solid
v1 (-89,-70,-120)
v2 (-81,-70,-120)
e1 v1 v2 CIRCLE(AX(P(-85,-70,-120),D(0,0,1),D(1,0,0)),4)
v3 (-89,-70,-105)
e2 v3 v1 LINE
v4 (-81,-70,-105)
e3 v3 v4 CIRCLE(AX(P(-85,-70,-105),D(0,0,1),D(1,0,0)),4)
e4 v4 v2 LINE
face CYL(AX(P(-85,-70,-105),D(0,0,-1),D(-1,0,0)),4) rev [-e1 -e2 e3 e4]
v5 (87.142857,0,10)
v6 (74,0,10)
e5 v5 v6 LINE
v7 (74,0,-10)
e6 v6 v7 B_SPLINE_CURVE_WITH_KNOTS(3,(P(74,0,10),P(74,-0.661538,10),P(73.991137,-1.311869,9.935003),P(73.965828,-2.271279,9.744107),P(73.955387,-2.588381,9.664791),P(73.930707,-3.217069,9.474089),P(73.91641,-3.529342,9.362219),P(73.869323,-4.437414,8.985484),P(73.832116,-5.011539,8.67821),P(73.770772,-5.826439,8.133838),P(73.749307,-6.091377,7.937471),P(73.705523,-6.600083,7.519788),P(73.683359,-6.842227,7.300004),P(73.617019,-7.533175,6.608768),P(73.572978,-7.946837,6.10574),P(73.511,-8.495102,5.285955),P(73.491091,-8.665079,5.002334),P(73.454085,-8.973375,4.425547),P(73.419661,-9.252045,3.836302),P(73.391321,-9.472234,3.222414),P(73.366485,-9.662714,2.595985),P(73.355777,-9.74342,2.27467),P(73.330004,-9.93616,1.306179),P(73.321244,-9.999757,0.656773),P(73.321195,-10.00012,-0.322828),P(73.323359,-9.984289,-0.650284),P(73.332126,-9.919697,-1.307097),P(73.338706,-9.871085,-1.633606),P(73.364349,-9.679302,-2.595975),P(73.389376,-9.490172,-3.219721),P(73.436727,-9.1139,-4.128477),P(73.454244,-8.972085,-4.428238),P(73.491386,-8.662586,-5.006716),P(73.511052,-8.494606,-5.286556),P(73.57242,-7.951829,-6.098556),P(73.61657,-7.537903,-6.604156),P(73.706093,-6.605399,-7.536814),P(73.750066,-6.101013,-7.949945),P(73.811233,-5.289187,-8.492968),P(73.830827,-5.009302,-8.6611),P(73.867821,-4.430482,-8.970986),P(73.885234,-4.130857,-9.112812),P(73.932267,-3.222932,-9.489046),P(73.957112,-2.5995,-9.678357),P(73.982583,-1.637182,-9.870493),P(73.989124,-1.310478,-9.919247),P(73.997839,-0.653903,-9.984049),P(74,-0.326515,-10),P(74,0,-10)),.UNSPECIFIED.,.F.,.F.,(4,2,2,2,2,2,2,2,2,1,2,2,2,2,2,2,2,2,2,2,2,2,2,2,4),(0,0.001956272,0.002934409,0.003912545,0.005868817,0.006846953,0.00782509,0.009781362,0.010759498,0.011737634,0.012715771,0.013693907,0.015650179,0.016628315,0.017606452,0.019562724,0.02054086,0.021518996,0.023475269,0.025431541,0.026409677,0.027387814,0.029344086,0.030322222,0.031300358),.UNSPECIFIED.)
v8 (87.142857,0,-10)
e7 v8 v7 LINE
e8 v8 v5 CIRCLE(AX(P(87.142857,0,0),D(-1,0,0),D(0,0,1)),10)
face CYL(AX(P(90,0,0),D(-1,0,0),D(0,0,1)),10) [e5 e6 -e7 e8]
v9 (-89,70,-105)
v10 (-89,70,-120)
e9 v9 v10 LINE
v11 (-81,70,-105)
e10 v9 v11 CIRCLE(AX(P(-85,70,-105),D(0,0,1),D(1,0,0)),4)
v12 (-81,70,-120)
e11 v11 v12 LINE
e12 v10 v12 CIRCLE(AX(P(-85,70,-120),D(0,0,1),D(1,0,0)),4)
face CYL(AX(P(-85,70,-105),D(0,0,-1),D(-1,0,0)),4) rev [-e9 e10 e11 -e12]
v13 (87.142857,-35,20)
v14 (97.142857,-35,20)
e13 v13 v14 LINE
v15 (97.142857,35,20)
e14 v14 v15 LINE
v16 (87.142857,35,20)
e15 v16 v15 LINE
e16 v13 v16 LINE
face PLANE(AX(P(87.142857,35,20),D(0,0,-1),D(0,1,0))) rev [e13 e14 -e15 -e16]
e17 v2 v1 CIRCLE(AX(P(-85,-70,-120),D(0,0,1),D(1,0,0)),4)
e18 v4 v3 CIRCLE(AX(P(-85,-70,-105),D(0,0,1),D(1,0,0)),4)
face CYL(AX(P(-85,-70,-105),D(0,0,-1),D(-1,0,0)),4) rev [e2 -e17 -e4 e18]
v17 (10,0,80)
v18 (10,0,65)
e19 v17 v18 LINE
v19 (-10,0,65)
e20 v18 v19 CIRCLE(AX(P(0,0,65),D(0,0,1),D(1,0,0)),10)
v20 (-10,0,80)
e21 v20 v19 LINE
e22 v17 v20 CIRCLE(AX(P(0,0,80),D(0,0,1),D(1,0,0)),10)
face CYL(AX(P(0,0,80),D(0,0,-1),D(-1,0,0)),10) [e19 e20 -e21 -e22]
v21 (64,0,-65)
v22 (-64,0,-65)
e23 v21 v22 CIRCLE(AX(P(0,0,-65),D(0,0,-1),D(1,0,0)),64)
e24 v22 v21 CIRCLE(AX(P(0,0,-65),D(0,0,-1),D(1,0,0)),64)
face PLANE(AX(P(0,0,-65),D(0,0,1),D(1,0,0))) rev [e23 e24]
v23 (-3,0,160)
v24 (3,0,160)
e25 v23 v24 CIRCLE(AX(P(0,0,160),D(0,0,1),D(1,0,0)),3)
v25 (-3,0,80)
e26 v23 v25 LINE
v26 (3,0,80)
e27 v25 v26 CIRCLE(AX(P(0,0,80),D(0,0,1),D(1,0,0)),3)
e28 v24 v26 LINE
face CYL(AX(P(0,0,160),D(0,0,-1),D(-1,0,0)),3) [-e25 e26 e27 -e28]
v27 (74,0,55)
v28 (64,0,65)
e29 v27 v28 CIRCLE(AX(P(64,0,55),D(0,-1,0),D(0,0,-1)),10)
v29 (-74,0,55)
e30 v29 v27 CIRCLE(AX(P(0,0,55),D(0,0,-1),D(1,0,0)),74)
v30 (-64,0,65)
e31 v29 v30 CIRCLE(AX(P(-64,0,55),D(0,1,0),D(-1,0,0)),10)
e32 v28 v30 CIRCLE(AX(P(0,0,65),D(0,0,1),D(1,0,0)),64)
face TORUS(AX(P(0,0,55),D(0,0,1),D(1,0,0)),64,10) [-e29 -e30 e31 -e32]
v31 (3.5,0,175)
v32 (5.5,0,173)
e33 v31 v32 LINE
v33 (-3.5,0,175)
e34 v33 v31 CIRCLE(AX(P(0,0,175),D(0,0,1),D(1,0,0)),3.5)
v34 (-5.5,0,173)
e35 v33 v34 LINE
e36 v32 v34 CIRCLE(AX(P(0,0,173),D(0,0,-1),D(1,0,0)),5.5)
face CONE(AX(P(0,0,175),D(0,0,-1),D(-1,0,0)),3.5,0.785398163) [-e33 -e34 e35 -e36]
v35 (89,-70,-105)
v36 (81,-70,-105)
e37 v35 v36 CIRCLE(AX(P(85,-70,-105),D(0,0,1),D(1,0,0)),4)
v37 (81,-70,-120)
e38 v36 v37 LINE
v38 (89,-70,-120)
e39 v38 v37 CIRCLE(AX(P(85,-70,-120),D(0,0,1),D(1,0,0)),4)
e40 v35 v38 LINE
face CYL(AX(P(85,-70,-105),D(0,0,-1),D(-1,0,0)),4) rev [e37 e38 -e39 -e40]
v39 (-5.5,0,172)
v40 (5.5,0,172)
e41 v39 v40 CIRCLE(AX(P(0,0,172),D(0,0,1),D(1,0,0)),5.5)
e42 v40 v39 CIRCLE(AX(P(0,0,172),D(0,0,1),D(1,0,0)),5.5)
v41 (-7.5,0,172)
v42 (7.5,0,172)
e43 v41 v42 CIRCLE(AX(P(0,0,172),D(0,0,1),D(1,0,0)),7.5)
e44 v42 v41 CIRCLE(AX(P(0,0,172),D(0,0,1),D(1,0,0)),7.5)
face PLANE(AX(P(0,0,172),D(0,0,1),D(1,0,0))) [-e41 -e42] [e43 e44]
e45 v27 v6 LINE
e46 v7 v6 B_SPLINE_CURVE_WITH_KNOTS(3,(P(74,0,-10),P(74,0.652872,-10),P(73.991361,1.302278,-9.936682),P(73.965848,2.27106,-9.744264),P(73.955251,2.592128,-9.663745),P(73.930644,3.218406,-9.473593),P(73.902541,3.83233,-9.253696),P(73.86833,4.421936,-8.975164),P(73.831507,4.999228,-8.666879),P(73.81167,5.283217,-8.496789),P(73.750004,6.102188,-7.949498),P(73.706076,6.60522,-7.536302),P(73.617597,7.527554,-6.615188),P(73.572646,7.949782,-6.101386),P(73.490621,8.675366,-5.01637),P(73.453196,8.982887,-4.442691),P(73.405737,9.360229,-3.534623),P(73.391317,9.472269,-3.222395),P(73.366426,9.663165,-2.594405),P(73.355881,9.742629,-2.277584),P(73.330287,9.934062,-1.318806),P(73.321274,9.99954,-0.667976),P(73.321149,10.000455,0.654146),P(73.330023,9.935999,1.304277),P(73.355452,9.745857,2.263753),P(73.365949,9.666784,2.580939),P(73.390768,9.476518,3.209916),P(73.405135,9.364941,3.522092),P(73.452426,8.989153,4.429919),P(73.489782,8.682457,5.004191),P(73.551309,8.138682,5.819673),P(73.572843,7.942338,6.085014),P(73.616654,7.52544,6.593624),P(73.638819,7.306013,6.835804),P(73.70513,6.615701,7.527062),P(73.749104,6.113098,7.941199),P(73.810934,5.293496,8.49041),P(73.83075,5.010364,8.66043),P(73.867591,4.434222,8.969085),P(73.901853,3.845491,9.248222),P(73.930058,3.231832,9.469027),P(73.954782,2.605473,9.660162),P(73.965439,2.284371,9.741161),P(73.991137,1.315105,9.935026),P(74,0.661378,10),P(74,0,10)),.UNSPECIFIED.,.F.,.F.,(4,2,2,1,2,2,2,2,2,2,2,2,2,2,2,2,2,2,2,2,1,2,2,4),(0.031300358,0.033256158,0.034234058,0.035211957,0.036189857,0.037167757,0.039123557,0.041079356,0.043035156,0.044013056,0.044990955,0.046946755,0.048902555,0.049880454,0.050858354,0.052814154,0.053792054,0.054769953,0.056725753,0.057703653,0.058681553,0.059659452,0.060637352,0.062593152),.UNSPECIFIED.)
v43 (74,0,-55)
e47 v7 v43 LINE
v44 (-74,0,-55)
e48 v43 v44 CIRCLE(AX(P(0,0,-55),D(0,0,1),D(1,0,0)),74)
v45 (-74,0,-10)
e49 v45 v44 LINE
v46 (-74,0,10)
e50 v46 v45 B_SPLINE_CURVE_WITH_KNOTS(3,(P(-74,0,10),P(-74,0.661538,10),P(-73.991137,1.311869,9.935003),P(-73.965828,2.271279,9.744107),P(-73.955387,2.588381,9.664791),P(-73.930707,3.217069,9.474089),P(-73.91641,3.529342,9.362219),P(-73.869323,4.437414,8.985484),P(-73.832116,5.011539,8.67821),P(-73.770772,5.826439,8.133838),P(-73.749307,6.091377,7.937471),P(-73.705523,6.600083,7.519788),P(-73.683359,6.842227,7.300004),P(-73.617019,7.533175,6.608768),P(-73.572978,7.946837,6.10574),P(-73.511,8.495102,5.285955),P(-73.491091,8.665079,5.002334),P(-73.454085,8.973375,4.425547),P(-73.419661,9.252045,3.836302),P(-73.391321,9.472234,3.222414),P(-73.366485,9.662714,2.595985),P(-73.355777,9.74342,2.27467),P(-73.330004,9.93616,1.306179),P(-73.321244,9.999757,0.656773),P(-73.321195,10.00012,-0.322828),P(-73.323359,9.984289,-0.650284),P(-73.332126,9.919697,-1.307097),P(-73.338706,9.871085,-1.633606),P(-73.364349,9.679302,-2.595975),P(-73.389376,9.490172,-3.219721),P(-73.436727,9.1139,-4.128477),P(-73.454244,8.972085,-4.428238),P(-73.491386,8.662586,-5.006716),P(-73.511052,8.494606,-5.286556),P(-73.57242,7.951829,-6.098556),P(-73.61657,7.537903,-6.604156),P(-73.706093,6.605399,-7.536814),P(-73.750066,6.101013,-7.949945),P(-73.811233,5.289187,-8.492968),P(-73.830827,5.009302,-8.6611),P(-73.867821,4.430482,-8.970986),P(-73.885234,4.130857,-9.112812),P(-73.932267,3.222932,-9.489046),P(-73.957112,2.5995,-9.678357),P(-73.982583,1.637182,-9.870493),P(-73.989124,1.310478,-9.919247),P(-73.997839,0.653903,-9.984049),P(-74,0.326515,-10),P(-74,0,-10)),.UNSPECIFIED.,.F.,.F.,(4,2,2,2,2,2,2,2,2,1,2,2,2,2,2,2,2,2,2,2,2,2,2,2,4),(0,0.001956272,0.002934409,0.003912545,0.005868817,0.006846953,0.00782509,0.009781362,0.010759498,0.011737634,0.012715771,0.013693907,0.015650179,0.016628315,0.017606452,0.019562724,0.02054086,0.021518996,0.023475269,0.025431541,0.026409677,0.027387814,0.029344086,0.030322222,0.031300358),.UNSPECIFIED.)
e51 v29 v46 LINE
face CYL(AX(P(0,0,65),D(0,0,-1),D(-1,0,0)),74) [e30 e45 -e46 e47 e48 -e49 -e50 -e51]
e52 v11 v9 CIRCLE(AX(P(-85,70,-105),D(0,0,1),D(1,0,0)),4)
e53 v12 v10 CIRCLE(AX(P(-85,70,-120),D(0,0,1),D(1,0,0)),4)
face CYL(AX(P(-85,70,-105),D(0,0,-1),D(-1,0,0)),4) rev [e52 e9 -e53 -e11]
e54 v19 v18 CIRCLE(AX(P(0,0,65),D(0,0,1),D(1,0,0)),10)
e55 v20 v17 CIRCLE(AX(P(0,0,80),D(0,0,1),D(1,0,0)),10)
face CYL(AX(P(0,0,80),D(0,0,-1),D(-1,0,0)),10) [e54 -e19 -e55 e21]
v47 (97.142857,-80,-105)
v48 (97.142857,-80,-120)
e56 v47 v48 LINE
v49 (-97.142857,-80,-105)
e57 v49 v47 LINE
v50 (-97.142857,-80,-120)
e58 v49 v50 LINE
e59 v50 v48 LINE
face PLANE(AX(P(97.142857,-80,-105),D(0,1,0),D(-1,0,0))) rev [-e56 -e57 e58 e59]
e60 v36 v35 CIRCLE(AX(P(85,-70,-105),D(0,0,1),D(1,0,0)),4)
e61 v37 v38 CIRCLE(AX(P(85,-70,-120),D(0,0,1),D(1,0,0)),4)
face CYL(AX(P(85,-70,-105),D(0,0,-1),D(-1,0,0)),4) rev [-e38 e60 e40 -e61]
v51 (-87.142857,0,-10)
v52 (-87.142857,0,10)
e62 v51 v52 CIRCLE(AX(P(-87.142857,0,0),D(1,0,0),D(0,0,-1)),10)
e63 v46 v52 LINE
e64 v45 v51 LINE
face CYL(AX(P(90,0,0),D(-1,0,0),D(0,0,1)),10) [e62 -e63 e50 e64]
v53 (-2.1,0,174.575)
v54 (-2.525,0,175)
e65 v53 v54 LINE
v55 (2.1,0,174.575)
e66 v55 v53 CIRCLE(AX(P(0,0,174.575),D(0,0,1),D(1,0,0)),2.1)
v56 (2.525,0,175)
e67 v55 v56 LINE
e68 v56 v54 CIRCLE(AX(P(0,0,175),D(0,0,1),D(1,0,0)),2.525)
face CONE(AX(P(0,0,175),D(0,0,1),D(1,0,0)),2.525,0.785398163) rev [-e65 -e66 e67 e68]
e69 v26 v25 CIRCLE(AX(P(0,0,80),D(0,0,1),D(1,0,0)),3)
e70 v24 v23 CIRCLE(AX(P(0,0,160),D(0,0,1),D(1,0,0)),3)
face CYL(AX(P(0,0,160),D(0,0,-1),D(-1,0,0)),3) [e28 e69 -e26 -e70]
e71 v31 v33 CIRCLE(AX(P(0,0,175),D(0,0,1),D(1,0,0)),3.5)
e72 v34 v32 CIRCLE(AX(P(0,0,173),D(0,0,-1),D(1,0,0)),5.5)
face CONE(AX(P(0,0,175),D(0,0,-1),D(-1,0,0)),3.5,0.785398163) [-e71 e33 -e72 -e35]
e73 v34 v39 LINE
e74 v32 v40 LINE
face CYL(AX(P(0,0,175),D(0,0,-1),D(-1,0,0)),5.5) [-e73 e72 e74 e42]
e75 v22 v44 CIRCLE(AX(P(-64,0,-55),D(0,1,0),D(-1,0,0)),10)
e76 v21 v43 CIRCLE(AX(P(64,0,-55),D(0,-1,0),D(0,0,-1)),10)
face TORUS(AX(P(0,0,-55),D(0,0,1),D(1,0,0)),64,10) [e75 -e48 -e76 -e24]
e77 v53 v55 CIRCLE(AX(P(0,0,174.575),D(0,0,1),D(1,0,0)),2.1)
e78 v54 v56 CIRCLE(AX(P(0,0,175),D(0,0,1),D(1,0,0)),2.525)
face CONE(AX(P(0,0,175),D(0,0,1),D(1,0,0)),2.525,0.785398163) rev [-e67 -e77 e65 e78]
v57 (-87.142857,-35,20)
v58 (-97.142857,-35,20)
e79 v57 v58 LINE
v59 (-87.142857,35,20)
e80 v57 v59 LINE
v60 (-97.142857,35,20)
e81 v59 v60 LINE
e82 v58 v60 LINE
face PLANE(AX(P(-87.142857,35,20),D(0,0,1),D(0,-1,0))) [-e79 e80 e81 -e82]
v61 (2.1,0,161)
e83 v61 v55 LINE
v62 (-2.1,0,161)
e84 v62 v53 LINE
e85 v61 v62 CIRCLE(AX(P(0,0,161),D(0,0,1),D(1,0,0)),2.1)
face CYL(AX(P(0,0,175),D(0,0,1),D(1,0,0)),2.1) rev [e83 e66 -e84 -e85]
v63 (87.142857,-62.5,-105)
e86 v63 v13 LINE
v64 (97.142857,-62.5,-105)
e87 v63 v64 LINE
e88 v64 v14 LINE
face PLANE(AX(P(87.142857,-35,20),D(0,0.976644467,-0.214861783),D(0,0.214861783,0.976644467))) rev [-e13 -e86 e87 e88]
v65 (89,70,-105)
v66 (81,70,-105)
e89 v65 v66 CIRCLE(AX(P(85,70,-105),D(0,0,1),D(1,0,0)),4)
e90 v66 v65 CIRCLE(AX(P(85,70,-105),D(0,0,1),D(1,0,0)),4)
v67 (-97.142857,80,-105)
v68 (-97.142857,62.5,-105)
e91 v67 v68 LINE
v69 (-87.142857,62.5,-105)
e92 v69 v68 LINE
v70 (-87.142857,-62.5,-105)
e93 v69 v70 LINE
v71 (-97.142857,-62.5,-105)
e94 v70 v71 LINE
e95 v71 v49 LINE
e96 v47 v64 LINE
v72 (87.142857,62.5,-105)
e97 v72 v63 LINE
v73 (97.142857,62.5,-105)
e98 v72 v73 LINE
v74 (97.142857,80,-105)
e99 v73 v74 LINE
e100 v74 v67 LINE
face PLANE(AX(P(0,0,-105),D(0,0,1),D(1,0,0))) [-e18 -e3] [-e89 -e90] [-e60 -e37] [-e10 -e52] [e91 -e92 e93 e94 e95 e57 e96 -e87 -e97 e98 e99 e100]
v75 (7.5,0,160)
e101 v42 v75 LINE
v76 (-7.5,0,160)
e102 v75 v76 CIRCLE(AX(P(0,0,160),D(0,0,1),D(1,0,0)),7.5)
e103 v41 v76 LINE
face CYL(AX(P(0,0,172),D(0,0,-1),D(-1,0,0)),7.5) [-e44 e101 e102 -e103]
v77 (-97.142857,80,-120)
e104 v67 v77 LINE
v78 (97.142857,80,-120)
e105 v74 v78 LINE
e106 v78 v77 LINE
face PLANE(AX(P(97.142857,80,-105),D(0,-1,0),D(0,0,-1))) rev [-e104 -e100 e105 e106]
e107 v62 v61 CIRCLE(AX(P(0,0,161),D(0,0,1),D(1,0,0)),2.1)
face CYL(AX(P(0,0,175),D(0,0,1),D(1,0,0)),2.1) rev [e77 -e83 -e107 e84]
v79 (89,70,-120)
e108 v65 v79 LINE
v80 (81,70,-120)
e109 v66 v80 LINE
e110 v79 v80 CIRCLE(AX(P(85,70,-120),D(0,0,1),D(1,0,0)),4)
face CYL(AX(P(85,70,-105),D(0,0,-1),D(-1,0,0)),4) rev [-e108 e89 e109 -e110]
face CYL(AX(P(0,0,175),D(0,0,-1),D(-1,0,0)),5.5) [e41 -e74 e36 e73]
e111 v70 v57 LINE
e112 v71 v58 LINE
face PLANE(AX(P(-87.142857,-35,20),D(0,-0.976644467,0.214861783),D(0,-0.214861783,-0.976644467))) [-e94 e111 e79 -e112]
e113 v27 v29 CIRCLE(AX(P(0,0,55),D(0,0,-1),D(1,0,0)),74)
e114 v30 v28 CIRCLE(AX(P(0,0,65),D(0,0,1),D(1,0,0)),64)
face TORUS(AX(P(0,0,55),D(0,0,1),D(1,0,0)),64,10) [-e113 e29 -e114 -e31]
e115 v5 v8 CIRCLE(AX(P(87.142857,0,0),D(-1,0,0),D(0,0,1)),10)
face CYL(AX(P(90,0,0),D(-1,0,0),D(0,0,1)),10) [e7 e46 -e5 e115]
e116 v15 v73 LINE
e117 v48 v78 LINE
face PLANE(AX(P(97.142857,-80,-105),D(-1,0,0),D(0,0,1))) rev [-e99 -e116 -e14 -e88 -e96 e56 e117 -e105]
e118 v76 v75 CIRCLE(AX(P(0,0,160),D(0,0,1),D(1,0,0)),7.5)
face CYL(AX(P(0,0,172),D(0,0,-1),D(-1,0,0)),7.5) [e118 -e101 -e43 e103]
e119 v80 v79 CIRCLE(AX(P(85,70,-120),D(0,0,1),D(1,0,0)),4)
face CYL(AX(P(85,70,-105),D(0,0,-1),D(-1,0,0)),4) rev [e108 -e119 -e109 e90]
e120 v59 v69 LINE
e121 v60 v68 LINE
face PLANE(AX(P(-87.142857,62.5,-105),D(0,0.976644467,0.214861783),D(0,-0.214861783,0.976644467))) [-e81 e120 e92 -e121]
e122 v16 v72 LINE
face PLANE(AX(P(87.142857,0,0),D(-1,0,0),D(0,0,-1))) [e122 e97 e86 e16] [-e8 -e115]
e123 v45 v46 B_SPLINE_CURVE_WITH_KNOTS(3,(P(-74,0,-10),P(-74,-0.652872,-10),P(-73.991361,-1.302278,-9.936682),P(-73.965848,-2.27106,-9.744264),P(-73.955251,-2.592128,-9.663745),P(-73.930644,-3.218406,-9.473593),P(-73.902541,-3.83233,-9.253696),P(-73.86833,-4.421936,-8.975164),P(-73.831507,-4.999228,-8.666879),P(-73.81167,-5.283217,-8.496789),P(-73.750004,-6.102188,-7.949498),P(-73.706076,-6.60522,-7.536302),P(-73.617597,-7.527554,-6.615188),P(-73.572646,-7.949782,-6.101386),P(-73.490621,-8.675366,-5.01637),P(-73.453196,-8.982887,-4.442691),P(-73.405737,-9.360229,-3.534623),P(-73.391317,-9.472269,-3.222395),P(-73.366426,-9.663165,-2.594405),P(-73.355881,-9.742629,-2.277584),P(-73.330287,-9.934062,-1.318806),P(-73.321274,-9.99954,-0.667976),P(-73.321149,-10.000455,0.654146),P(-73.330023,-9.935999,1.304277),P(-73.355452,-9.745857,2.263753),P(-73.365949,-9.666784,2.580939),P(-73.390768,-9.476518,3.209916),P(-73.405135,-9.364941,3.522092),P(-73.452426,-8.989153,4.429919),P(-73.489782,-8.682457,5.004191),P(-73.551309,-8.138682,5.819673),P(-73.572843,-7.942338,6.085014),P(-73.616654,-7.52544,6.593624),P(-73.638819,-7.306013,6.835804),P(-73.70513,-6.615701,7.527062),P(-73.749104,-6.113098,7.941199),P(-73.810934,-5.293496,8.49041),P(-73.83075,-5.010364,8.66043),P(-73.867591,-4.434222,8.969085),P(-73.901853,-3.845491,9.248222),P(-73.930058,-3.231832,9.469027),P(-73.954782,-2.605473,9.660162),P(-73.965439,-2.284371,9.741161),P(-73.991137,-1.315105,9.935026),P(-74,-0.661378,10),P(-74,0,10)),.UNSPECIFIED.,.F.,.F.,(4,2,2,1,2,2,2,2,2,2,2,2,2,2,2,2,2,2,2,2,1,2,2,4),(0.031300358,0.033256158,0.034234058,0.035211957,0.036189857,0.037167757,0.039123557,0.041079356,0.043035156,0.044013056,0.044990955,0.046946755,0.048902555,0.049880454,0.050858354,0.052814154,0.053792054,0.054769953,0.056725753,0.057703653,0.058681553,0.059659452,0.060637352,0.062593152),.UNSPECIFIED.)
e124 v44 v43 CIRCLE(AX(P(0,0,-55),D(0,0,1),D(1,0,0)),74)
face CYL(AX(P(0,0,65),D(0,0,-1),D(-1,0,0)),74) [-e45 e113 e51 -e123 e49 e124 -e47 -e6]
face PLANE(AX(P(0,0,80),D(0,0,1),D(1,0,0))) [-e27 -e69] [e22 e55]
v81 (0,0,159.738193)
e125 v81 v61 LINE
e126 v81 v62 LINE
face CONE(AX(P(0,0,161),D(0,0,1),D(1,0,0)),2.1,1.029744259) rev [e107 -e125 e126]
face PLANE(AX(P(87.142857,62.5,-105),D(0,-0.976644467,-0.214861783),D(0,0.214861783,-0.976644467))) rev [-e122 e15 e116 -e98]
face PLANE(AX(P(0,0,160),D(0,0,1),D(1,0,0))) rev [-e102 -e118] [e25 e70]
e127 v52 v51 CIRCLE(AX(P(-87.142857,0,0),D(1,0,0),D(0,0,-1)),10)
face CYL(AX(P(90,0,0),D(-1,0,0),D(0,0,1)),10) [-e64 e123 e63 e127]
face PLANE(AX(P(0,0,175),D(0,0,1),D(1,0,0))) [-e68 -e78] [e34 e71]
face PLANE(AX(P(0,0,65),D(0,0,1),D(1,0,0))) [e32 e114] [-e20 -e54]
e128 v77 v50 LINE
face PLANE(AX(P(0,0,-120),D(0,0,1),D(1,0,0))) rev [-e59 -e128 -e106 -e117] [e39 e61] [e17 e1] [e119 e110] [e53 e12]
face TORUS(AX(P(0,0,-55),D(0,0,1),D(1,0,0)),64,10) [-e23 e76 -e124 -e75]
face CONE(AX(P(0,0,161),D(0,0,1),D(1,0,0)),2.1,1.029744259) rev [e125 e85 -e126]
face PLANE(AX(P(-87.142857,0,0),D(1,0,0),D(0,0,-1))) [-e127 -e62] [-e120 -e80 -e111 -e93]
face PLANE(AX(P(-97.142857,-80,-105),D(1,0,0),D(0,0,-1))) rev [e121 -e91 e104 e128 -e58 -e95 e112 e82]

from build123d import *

# Parameters (mm, degrees)
SKETCH1_R                   = 74
BOSS_EXTRUDE1_DEPTH         = 65
FILLET1_R                   = 10
SKETCH2_R                   = 10
BOSS_EXTRUDE2_DEPTH         = 15
BOSS_EXTRUDE3_START         = -200
SKETCH3_W                   = 194.285714286
SKETCH3_H                   = 160
SKETCH3_R                   = 4
BOSS_EXTRUDE3_DEPTH         = 15
BOSS_EXTRUDE4_DEPTH         = 10
SKETCH5_R                   = 10
BOSS_EXTRUDE5_DEPTH         = 90
SKETCH6_R                   = 3
BOSS_EXTRUDE6_DEPTH         = 80
SKETCH7_R                   = 7.5
BOSS_EXTRUDE7_DEPTH         = 12
SKETCH8_R                   = 5.5
BOSS_EXTRUDE8_DEPTH         = 3
CHAMFER1_SIZE               = 2
M5_TAPPED_HOLE1_D           = 4.2
M5_TAPPED_HOLE1_DEPTH       = 14
M5_TAPPED_HOLE1_CSINK_D     = 5.05
M5_TAPPED_HOLE1_CSINK_ANGLE = 90
M5_TAPPED_HOLE1_TIP         = 1.2618073


with BuildPart() as part:
    # Sketch1 → Boss-Extrude1 (new, symmetric)
    with BuildSketch(Plane.XY):
        Circle(SKETCH1_R)
    extrude(amount=BOSS_EXTRUDE1_DEPTH, both=True)

    # Fillet1
    fillet1_edges = [part.edges().sort_by_distance(p)[0] for p in [
        (-74, 0, -65),
        (-74, 0, 65),
    ]]
    fillet(fillet1_edges, radius=FILLET1_R)

    # Sketch2 → Boss-Extrude2 (add)
    with BuildSketch(Plane.XY.offset(65)):
        Circle(SKETCH2_R)
    extrude(amount=BOSS_EXTRUDE2_DEPTH)



with BuildPart() as body_2:
    # Sketch3 → Boss-Extrude3 (new body)
    with BuildSketch(Plane.XY.offset(80).offset(BOSS_EXTRUDE3_START)):
        Rectangle(SKETCH3_W, SKETCH3_H)
        with Locations((-85, 70)):
            Circle(SKETCH3_R, mode=Mode.SUBTRACT)
        with Locations((85, 70)):
            Circle(SKETCH3_R, mode=Mode.SUBTRACT)
        with Locations((85, -70)):
            Circle(SKETCH3_R, mode=Mode.SUBTRACT)
        with Locations((-85, -70)):
            Circle(SKETCH3_R, mode=Mode.SUBTRACT)
    extrude(amount=BOSS_EXTRUDE3_DEPTH)

    # Sketch4 → Boss-Extrude4 (add)
    with BuildSketch(Plane.ZY.offset(97.142857143)):
        Polygon((-105, 62.5), (20, 35), (20, -35), (-105, -62.5), align=None)
    boss_extrude4 = extrude(amount=-BOSS_EXTRUDE4_DEPTH)

    # Mirror1: Boss-Extrude4 across plane
    add(boss_extrude4.mirror(Plane(origin=(0, 0, 0), x_dir=(0, 0, 1), z_dir=(1, 0, 0))))


with BuildPart() as part_1:
    add(part.part)

    add(body_2.part)  # Boss-Extrude5 merges body 2
    # Sketch5 → Boss-Extrude5 (add, symmetric)
    with BuildSketch(Plane(origin=(0, 0, 0), x_dir=(0, 0, -1), z_dir=(1, 0, 0))):
        with Locations(Location((0, 0, 0), (0, 0, 180))):
            Circle(SKETCH5_R)
    extrude(amount=BOSS_EXTRUDE5_DEPTH, both=True)

    # Sketch6 → Boss-Extrude6 (add)
    with BuildSketch(Plane.XY.offset(80)):
        Circle(SKETCH6_R)
    extrude(amount=BOSS_EXTRUDE6_DEPTH)

    # Sketch7 → Boss-Extrude7 (add)
    with BuildSketch(Plane.XY.offset(160)):
        Circle(SKETCH7_R)
    extrude(amount=BOSS_EXTRUDE7_DEPTH)

    # Sketch8 → Boss-Extrude8 (add)
    with BuildSketch(Plane.XY.offset(172)):
        Circle(SKETCH8_R)
    extrude(amount=BOSS_EXTRUDE8_DEPTH)

    # Chamfer1
    chamfer1_edges = [part_1.edges().sort_by_distance(p)[0] for p in [
        (-5.5, 0, 175),
    ]]
    chamfer(chamfer1_edges, length=CHAMFER1_SIZE)

    # M5 Tapped Hole1
    with Locations(Plane.XY.offset(175)):
        with Locations((0, 0)):
            CounterSinkHole(M5_TAPPED_HOLE1_D / 2, M5_TAPPED_HOLE1_CSINK_D / 2, depth=M5_TAPPED_HOLE1_DEPTH, counter_sink_angle=M5_TAPPED_HOLE1_CSINK_ANGLE)
            with Locations((0, 0, -(M5_TAPPED_HOLE1_DEPTH + M5_TAPPED_HOLE1_TIP / 2))):  # 118° drill point
                Cone(0, M5_TAPPED_HOLE1_D / 2, M5_TAPPED_HOLE1_TIP, mode=Mode.SUBTRACT)


solid = part_1.part
